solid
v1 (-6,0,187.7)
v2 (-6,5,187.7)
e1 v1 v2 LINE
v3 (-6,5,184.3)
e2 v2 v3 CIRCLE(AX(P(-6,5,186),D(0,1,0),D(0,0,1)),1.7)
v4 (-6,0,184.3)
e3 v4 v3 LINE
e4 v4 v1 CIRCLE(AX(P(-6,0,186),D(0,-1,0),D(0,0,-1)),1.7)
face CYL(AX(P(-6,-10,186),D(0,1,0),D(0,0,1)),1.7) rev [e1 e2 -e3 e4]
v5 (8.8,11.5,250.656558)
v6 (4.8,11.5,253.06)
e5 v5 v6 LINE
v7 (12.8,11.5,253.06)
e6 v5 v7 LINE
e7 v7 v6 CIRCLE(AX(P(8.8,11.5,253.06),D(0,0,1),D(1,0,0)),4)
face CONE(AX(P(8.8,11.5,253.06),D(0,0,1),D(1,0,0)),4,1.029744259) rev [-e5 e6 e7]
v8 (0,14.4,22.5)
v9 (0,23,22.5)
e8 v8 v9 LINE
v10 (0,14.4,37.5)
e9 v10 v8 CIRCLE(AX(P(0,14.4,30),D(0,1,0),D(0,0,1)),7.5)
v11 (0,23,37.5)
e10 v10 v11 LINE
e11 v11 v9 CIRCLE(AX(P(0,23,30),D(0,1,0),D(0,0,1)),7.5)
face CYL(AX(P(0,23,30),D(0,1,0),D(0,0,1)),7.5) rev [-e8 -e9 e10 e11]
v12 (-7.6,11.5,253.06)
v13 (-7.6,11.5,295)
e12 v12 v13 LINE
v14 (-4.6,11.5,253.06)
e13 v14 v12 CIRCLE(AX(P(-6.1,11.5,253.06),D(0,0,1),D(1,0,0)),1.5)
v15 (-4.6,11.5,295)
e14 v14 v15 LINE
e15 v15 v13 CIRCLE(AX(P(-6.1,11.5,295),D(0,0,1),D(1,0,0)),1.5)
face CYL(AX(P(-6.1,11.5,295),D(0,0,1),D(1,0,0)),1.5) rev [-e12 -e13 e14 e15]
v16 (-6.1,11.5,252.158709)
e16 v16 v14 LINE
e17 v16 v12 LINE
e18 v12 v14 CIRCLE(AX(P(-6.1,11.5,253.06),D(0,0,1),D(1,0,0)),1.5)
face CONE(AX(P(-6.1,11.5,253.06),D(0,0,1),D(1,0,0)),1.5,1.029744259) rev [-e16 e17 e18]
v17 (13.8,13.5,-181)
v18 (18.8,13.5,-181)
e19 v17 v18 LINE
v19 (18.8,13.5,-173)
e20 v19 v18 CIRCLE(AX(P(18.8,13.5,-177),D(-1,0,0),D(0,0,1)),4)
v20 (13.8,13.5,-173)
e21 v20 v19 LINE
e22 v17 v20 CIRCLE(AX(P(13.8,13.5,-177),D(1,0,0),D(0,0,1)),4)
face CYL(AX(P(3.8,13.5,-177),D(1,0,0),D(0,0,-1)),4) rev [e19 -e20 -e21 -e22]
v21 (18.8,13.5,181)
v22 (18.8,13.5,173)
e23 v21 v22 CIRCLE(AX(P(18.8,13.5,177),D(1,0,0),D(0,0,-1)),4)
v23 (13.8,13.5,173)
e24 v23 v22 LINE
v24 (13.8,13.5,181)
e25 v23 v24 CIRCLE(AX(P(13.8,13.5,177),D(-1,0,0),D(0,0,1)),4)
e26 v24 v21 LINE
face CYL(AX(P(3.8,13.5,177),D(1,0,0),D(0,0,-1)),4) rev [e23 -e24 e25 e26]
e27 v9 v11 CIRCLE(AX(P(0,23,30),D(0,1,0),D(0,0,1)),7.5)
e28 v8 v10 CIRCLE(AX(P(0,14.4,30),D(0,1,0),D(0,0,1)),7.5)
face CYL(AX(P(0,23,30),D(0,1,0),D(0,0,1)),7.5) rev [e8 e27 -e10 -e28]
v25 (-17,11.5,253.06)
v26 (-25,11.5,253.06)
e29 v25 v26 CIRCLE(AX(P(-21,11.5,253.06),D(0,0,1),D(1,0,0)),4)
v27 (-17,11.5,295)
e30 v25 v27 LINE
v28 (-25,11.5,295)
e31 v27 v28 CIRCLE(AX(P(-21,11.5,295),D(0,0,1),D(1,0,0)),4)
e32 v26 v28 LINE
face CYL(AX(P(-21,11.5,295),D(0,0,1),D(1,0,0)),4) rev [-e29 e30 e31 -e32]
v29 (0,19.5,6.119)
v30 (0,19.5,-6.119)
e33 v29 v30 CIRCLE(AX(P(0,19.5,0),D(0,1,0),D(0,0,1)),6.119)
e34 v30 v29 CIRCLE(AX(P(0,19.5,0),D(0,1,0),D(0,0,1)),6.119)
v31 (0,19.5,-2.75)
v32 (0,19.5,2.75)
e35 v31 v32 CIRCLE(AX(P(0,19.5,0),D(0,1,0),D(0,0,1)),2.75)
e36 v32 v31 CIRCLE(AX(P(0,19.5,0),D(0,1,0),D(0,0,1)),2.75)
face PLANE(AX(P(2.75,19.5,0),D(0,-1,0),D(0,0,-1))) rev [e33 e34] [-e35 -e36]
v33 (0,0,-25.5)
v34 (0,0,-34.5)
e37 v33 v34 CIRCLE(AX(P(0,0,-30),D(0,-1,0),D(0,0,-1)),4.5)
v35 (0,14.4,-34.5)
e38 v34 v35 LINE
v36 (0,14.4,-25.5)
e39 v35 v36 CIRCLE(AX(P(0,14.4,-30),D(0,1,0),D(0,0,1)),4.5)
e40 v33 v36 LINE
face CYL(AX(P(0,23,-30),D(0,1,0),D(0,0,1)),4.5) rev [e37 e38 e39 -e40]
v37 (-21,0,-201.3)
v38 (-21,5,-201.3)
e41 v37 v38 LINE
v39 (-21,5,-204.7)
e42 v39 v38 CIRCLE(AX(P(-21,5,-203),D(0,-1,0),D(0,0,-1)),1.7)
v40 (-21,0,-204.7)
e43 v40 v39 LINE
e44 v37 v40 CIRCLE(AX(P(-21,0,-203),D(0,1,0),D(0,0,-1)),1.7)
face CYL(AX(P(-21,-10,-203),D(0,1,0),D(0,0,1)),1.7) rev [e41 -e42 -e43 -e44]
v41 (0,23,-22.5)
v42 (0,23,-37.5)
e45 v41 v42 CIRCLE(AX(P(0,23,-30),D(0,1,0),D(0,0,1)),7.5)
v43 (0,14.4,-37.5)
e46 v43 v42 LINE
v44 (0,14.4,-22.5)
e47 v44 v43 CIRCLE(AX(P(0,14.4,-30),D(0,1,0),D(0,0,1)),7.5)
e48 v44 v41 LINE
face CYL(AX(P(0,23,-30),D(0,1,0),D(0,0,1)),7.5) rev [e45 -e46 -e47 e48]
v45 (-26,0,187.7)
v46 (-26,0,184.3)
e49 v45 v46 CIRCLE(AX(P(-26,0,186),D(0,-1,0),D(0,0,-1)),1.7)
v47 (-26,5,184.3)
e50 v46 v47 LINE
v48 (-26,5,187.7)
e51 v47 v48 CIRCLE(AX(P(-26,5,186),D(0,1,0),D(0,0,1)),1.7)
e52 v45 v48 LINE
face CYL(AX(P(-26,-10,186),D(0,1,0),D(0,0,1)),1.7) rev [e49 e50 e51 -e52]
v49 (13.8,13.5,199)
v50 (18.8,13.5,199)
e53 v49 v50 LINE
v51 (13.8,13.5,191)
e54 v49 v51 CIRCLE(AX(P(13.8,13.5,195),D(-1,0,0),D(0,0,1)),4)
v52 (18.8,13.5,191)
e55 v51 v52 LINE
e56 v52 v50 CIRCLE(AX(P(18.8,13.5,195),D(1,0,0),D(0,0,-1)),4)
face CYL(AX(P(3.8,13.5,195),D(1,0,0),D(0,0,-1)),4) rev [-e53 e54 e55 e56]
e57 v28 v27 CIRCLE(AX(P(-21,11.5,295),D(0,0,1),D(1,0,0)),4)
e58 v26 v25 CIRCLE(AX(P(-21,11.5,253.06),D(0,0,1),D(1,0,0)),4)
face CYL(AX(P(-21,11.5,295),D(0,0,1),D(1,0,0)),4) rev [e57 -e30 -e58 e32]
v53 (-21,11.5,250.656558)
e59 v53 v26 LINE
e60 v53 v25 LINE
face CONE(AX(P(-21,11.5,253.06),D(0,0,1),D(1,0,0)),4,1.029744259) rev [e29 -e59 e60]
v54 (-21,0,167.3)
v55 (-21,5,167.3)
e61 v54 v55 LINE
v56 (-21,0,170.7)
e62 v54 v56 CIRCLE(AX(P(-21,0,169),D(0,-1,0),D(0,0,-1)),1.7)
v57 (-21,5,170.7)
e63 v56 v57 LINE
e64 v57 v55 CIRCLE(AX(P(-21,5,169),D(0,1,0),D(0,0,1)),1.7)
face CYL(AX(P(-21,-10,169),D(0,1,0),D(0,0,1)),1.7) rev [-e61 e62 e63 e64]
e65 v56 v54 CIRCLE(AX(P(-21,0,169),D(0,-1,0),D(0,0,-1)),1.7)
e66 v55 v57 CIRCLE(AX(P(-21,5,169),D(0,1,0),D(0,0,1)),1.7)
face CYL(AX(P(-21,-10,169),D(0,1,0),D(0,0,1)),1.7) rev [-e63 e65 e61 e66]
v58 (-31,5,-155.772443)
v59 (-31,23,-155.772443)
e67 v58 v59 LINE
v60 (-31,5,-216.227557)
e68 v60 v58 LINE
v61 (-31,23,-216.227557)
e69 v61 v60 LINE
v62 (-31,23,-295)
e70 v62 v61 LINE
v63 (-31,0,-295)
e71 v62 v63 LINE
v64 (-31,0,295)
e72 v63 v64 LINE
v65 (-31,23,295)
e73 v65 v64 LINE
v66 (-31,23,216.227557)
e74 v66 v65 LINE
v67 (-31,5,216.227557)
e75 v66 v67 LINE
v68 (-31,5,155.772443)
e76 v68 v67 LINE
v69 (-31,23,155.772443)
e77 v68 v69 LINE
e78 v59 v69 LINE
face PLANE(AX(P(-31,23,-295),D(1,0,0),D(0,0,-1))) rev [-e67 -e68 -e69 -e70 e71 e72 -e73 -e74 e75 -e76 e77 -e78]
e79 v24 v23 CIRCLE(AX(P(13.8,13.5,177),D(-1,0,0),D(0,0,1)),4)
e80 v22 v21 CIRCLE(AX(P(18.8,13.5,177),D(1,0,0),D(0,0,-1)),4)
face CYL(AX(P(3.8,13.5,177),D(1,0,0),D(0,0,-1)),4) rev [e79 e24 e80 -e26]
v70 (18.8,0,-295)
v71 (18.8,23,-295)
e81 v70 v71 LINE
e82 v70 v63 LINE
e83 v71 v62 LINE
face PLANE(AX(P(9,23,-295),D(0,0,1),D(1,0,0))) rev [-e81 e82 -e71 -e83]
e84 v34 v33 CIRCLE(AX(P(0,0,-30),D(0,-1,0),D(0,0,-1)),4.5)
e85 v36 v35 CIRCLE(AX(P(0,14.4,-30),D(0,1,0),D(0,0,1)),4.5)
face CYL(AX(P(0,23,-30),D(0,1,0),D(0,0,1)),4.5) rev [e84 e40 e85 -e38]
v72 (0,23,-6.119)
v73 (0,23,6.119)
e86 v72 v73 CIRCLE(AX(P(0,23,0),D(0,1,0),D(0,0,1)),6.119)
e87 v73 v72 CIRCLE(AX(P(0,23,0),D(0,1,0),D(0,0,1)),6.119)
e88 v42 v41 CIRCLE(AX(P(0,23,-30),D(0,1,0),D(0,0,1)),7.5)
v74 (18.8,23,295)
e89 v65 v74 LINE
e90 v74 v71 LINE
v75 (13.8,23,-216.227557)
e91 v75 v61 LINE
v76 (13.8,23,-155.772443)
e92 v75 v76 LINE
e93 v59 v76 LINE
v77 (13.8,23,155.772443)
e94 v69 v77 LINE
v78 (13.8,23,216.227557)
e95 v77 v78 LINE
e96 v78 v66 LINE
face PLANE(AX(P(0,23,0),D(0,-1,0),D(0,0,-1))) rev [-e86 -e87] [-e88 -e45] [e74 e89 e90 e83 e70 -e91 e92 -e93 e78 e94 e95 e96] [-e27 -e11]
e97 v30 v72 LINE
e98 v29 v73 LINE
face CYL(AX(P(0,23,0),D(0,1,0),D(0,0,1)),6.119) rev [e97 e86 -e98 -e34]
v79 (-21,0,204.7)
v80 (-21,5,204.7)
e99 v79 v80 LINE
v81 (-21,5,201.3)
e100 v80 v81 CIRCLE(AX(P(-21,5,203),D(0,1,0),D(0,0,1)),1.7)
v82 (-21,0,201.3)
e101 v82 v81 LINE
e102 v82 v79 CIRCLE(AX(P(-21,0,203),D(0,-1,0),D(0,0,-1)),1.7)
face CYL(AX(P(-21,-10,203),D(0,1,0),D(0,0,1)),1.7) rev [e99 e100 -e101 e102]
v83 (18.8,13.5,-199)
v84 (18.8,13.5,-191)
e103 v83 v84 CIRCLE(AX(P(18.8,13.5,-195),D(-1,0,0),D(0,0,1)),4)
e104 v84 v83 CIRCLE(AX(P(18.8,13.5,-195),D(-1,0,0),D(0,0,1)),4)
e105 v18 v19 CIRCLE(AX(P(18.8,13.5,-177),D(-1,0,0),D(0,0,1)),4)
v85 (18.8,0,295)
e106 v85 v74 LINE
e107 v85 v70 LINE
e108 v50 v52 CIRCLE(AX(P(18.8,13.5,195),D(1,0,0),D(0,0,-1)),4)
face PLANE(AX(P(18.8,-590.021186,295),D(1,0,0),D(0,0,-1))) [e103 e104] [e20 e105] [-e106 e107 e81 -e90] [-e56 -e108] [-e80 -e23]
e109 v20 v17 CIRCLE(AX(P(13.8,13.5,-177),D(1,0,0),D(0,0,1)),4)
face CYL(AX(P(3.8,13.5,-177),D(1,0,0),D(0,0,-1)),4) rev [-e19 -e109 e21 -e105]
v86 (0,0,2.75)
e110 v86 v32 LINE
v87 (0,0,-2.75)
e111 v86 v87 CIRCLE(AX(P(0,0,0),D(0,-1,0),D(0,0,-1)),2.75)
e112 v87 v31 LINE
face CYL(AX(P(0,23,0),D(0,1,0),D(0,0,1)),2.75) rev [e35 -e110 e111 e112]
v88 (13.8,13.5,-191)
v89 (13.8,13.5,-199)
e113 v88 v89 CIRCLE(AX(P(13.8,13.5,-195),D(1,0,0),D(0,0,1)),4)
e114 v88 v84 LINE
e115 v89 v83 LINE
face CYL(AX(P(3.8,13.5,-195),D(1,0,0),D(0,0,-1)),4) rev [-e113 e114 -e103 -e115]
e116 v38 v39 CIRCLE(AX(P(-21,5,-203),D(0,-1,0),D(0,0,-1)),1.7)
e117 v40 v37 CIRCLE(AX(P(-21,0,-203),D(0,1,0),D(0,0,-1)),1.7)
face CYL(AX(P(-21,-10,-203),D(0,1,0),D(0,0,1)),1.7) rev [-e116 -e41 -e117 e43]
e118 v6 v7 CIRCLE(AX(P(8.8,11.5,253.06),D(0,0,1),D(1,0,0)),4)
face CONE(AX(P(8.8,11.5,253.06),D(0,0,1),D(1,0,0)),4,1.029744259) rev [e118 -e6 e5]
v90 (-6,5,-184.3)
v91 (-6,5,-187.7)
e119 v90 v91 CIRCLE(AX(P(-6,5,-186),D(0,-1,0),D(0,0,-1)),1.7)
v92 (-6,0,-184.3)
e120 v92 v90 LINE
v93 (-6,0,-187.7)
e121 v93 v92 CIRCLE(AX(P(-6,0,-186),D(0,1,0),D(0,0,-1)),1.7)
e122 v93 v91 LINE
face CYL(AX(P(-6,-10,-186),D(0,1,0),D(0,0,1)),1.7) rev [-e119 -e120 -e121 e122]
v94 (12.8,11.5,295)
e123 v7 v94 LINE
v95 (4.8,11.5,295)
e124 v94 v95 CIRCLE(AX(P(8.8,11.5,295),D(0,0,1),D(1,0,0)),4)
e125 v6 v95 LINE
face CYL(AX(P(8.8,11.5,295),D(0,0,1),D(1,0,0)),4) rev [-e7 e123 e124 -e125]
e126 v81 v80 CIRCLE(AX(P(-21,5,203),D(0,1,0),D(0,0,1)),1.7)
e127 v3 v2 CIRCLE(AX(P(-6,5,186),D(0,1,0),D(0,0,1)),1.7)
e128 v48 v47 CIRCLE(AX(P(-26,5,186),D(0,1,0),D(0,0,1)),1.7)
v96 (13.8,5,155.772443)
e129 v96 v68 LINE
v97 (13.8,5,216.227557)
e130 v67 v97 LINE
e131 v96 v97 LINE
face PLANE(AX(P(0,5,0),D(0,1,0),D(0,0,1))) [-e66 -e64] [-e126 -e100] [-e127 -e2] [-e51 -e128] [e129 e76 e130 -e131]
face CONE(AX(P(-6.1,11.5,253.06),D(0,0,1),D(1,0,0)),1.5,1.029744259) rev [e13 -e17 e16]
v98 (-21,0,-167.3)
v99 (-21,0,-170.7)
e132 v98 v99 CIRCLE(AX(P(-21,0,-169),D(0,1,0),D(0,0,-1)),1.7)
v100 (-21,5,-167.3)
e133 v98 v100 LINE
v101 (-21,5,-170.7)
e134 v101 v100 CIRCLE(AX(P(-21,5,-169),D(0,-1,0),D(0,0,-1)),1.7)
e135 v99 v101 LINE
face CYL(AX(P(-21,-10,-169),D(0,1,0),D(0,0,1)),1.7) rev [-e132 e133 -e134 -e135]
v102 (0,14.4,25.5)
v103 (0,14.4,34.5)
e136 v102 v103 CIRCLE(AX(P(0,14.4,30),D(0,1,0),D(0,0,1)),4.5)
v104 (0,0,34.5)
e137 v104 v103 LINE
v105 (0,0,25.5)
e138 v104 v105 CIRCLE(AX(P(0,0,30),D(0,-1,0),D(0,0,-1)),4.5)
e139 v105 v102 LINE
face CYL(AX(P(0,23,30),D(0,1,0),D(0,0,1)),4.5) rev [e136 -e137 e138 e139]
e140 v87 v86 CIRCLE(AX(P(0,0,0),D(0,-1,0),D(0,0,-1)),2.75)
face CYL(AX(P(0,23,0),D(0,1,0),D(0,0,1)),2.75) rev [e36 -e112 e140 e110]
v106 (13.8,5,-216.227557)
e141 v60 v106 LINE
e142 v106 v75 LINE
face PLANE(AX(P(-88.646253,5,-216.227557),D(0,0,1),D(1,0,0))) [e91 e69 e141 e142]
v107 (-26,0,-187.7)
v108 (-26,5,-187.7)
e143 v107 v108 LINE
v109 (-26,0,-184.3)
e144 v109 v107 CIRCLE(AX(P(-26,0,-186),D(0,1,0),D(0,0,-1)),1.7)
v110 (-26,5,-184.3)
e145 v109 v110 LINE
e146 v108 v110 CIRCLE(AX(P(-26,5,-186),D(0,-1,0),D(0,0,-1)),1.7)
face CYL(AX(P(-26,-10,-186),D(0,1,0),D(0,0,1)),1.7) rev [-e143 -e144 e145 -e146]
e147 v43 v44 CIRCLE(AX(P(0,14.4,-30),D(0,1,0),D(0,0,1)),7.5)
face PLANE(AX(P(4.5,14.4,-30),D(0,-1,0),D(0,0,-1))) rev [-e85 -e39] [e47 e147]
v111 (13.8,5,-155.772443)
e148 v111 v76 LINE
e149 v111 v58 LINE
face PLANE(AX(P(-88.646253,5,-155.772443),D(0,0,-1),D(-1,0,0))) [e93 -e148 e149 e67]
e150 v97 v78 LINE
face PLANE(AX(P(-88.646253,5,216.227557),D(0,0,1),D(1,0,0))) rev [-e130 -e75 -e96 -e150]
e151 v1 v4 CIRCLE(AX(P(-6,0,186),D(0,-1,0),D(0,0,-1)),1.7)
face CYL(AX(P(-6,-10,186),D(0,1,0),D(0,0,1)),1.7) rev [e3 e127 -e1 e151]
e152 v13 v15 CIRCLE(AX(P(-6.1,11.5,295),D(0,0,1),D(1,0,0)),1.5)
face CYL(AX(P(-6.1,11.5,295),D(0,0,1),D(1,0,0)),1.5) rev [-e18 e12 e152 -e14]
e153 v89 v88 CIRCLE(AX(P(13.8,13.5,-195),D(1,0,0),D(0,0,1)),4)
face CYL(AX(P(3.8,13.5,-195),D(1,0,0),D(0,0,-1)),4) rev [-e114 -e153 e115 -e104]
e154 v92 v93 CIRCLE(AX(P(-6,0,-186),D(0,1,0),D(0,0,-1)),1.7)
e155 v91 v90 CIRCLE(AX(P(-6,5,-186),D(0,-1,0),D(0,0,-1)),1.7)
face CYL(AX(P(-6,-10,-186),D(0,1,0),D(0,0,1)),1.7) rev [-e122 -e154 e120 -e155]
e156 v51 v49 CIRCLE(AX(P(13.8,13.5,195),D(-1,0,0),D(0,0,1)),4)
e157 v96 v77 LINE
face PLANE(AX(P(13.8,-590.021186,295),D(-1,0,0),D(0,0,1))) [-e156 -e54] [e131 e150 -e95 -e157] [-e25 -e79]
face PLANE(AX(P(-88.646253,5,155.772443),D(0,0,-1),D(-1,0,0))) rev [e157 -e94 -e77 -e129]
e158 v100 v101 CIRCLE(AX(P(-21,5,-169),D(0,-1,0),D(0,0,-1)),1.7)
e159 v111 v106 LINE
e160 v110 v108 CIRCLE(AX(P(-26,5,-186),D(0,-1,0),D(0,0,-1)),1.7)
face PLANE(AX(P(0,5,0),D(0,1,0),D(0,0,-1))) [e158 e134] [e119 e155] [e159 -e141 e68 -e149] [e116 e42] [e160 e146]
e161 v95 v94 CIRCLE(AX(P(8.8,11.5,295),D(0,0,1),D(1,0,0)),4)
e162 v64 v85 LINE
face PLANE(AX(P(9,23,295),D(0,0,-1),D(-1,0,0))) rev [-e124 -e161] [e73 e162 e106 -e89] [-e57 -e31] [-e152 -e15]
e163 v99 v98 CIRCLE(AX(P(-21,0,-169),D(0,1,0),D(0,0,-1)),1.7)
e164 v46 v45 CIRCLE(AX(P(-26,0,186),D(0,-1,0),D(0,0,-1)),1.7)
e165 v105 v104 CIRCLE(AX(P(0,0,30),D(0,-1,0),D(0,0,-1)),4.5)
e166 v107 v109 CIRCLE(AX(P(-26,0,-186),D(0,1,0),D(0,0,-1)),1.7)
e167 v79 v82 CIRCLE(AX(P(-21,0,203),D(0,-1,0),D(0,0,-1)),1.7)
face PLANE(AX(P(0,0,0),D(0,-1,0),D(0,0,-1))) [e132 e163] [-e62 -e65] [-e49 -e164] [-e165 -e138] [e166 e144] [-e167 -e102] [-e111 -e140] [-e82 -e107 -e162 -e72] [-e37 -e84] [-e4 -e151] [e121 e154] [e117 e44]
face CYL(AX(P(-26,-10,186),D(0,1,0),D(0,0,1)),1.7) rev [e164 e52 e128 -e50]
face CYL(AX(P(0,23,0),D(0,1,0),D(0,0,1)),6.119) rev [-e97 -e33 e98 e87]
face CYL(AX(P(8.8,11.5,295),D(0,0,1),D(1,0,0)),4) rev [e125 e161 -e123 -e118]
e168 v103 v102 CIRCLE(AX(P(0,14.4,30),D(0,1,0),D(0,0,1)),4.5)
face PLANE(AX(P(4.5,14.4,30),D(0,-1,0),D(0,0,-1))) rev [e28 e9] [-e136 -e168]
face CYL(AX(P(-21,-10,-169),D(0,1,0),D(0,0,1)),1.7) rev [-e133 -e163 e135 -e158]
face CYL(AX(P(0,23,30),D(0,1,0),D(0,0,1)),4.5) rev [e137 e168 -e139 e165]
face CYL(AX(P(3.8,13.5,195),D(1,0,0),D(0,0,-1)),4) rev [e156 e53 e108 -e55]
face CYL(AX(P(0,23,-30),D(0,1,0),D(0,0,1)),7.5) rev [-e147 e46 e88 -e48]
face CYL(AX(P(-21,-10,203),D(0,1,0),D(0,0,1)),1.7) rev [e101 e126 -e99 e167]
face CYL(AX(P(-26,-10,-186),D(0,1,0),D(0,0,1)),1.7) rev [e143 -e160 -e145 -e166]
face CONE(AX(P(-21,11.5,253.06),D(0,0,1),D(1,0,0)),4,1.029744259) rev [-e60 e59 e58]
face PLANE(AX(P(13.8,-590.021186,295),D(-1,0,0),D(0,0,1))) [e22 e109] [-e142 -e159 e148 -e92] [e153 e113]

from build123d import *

# Parameters (mm, degrees)
SKETCH1_W                                           = 40
SKETCH1_H                                           = 590
BOSS_EXTRUDE1_DEPTH                                 = 23
CBORE_FOR_M8_HEX_SOCKET_HEAD_CAP_SCREW0_D           = 9
CBORE_FOR_M8_HEX_SOCKET_HEAD_CAP_SCREW0_DEPTH       = 41.94
CBORE_FOR_M8_HEX_SOCKET_HEAD_CAP_SCREW0_CBORE_D     = 15
CBORE_FOR_M8_HEX_SOCKET_HEAD_CAP_SCREW0_CBORE_DEPTH = 8.6
CBORE_FOR_M8_HEX_SOCKET_HEAD_CAP_SCREW0_TIP         = 2.703872786
SKETCH9_W                                           = 125.292505666
SKETCH9_H                                           = 60.455114524
CUT_EXTRUDE1_DEPTH                                  = 18
SKETCH11_W                                          = 4.8
SKETCH11_H                                          = 78.772442738
SKETCH11_H_2                                        = 311.544885476
BOSS_EXTRUDE2_DEPTH                                 = 23
SKETCH12_W                                          = 60.455114524
SKETCH12_H                                          = 5
BOSS_EXTRUDE3_DEPTH                                 = 4.8
SKETCH13_W                                          = 5
SKETCH13_H                                          = 590
BOSS_EXTRUDE4_DEPTH                                 = 23
SKETCH14_R                                          = 4
CUT_EXTRUDE2_DEPTH                                  = 15
SKETCH15_R                                          = 1.7
CUT_EXTRUDE3_DEPTH                                  = 15
CBORE_FOR_M5_HEX_HEAD_BOLT1_D                       = 5.5
CBORE_FOR_M5_HEX_HEAD_BOLT1_DEPTH                   = 41.94
CBORE_FOR_M5_HEX_HEAD_BOLT1_CBORE_D                 = 12.238
CBORE_FOR_M5_HEX_HEAD_BOLT1_CBORE_DEPTH             = 3.5
CBORE_FOR_M5_HEX_HEAD_BOLT1_TIP                     = 1.652366702
F_8_0MM_DOWEL_HOLE1_D                               = 8
F_8_0MM_DOWEL_HOLE1_DEPTH                           = 41.94
F_8_0MM_DOWEL_HOLE1_TIP                             = 2.403442476
F_3_0MM_DOWEL_HOLE1_D                               = 3
F_3_0MM_DOWEL_HOLE1_DEPTH                           = 41.94
F_3_0MM_DOWEL_HOLE1_TIP                             = 0.901290929


with BuildPart() as part:
    # Sketch1 → Boss-Extrude1 (new body)
    with BuildSketch(Plane(origin=(0, 0, 0), x_dir=(1, 0, 0), z_dir=(0, 1, 0))):
        with Locations((-11, 0)):
            Rectangle(SKETCH1_W, SKETCH1_H)
    extrude(amount=BOSS_EXTRUDE1_DEPTH)

    # CBORE for M8 Hex Socket Head Cap Screw0
    with Locations(Plane(origin=(0, 23, 30), x_dir=(0, 0, 1), z_dir=(0, 1, 0))):
        with Locations((0, 0), (-60, 0)):
            CounterBoreHole(CBORE_FOR_M8_HEX_SOCKET_HEAD_CAP_SCREW0_D / 2, CBORE_FOR_M8_HEX_SOCKET_HEAD_CAP_SCREW0_CBORE_D / 2, CBORE_FOR_M8_HEX_SOCKET_HEAD_CAP_SCREW0_CBORE_DEPTH, depth=CBORE_FOR_M8_HEX_SOCKET_HEAD_CAP_SCREW0_DEPTH)
            with Locations((0, 0, -(CBORE_FOR_M8_HEX_SOCKET_HEAD_CAP_SCREW0_DEPTH + CBORE_FOR_M8_HEX_SOCKET_HEAD_CAP_SCREW0_TIP / 2))):  # 118° drill point
                Cone(0, CBORE_FOR_M8_HEX_SOCKET_HEAD_CAP_SCREW0_D / 2, CBORE_FOR_M8_HEX_SOCKET_HEAD_CAP_SCREW0_TIP, mode=Mode.SUBTRACT)

    # Sketch9 → Cut-Extrude1 (cut)
    with BuildSketch(Plane(origin=(0, 23, 0), x_dir=(1, 0, 0), z_dir=(0, 1, 0))):
        with Locations((-26, -186)):
            Rectangle(SKETCH9_W, SKETCH9_H)
    cut_extrude1 = extrude(amount=-CUT_EXTRUDE1_DEPTH, mode=Mode.SUBTRACT)

    # Mirror1: Cut-Extrude1 across plane
    add(cut_extrude1.mirror(Plane.XY), mode=Mode.SUBTRACT)

    # Sketch11 → Boss-Extrude2 (add)
    with BuildSketch(Plane(origin=(0, 23, 0), x_dir=(1, 0, 0), z_dir=(0, 1, 0))):
        with Locations((11.4, -255.613778631)):
            Rectangle(SKETCH11_W, SKETCH11_H)
        with Locations((11.4, 255.613778631)):
            Rectangle(SKETCH11_W, SKETCH11_H)
        with Locations((11.4, 0)):
            Rectangle(SKETCH11_W, SKETCH11_H_2)
    extrude(amount=-BOSS_EXTRUDE2_DEPTH)

    # Sketch12 → Boss-Extrude3 (add)
    with BuildSketch(Plane(origin=(9, 0, 0), x_dir=(0, 0, -1), z_dir=(1, 0, 0))):
        with Locations((-186, 2.5)):
            Rectangle(SKETCH12_W, SKETCH12_H)
    boss_extrude3 = extrude(amount=BOSS_EXTRUDE3_DEPTH)

    # Mirror2: Boss-Extrude3 across plane
    add(boss_extrude3.mirror(Plane.XY))

    # Sketch13 → Boss-Extrude4 (add)
    with BuildSketch(Plane(origin=(0, 23, 0), x_dir=(1, 0, 0), z_dir=(0, 1, 0))):
        with Locations((16.3, 0)):
            Rectangle(SKETCH13_W, SKETCH13_H)
    extrude(amount=-BOSS_EXTRUDE4_DEPTH)

    # Sketch14 → Cut-Extrude2 (cut)
    with BuildSketch(Plane(origin=(18.8, 0, 0), x_dir=(0, 0, -1), z_dir=(1, 0, 0))):
        with Locations((-195, 13.5)):
            Circle(SKETCH14_R)
        with Locations((-177, 13.5)):
            Circle(SKETCH14_R)
    cut_extrude2 = extrude(amount=-CUT_EXTRUDE2_DEPTH, mode=Mode.SUBTRACT)

    # Mirror3: Cut-Extrude2 across plane
    add(cut_extrude2.mirror(Plane.XY), mode=Mode.SUBTRACT)

    # Sketch15 → Cut-Extrude3 (cut)
    with BuildSketch(Plane(origin=(0, 5, 0), x_dir=(1, 0, 0), z_dir=(0, 1, 0))):
        with Locations(Location((-21, -169, 0), (0, 0, 270))):
            Circle(SKETCH15_R)
        with Locations(Location((-6, -186, 0), (0, 0, 270))):
            Circle(SKETCH15_R)
        with Locations(Location((-26, -186, 0), (0, 0, 270))):
            Circle(SKETCH15_R)
        with Locations(Location((-21, -203, 0), (0, 0, 270))):
            Circle(SKETCH15_R)
    cut_extrude3 = extrude(amount=-CUT_EXTRUDE3_DEPTH, mode=Mode.SUBTRACT)

    # Mirror4: Cut-Extrude3 across plane
    add(cut_extrude3.mirror(Plane.XY), mode=Mode.SUBTRACT)

    # CBORE for M5 Hex Head Bolt1
    with Locations(Plane.ZX.offset(23)):
        with Locations((0, 0)):
            CounterBoreHole(CBORE_FOR_M5_HEX_HEAD_BOLT1_D / 2, CBORE_FOR_M5_HEX_HEAD_BOLT1_CBORE_D / 2, CBORE_FOR_M5_HEX_HEAD_BOLT1_CBORE_DEPTH, depth=CBORE_FOR_M5_HEX_HEAD_BOLT1_DEPTH)
            with Locations((0, 0, -(CBORE_FOR_M5_HEX_HEAD_BOLT1_DEPTH + CBORE_FOR_M5_HEX_HEAD_BOLT1_TIP / 2))):  # 118° drill point
                Cone(0, CBORE_FOR_M5_HEX_HEAD_BOLT1_D / 2, CBORE_FOR_M5_HEX_HEAD_BOLT1_TIP, mode=Mode.SUBTRACT)

    # Ø8.0mm Dowel Hole1
    with Locations(Plane(origin=(-21, 11.5, 295), x_dir=(1, 0, 0), z_dir=(0, 0, 1))):
        with Locations((0, 0), (29.8, 0)):
            Hole(F_8_0MM_DOWEL_HOLE1_D / 2, depth=F_8_0MM_DOWEL_HOLE1_DEPTH)
            with Locations((0, 0, -(F_8_0MM_DOWEL_HOLE1_DEPTH + F_8_0MM_DOWEL_HOLE1_TIP / 2))):  # 118° drill point
                Cone(0, F_8_0MM_DOWEL_HOLE1_D / 2, F_8_0MM_DOWEL_HOLE1_TIP, mode=Mode.SUBTRACT)

    # Ø3.0mm Dowel Hole1
    with Locations(Plane(origin=(-6.1, 11.5, 295), x_dir=(1, 0, 0), z_dir=(0, 0, 1))):
        with Locations((0, 0)):
            Hole(F_3_0MM_DOWEL_HOLE1_D / 2, depth=F_3_0MM_DOWEL_HOLE1_DEPTH)
            with Locations((0, 0, -(F_3_0MM_DOWEL_HOLE1_DEPTH + F_3_0MM_DOWEL_HOLE1_TIP / 2))):  # 118° drill point
                Cone(0, F_3_0MM_DOWEL_HOLE1_D / 2, F_3_0MM_DOWEL_HOLE1_TIP, mode=Mode.SUBTRACT)


solid = part.part
